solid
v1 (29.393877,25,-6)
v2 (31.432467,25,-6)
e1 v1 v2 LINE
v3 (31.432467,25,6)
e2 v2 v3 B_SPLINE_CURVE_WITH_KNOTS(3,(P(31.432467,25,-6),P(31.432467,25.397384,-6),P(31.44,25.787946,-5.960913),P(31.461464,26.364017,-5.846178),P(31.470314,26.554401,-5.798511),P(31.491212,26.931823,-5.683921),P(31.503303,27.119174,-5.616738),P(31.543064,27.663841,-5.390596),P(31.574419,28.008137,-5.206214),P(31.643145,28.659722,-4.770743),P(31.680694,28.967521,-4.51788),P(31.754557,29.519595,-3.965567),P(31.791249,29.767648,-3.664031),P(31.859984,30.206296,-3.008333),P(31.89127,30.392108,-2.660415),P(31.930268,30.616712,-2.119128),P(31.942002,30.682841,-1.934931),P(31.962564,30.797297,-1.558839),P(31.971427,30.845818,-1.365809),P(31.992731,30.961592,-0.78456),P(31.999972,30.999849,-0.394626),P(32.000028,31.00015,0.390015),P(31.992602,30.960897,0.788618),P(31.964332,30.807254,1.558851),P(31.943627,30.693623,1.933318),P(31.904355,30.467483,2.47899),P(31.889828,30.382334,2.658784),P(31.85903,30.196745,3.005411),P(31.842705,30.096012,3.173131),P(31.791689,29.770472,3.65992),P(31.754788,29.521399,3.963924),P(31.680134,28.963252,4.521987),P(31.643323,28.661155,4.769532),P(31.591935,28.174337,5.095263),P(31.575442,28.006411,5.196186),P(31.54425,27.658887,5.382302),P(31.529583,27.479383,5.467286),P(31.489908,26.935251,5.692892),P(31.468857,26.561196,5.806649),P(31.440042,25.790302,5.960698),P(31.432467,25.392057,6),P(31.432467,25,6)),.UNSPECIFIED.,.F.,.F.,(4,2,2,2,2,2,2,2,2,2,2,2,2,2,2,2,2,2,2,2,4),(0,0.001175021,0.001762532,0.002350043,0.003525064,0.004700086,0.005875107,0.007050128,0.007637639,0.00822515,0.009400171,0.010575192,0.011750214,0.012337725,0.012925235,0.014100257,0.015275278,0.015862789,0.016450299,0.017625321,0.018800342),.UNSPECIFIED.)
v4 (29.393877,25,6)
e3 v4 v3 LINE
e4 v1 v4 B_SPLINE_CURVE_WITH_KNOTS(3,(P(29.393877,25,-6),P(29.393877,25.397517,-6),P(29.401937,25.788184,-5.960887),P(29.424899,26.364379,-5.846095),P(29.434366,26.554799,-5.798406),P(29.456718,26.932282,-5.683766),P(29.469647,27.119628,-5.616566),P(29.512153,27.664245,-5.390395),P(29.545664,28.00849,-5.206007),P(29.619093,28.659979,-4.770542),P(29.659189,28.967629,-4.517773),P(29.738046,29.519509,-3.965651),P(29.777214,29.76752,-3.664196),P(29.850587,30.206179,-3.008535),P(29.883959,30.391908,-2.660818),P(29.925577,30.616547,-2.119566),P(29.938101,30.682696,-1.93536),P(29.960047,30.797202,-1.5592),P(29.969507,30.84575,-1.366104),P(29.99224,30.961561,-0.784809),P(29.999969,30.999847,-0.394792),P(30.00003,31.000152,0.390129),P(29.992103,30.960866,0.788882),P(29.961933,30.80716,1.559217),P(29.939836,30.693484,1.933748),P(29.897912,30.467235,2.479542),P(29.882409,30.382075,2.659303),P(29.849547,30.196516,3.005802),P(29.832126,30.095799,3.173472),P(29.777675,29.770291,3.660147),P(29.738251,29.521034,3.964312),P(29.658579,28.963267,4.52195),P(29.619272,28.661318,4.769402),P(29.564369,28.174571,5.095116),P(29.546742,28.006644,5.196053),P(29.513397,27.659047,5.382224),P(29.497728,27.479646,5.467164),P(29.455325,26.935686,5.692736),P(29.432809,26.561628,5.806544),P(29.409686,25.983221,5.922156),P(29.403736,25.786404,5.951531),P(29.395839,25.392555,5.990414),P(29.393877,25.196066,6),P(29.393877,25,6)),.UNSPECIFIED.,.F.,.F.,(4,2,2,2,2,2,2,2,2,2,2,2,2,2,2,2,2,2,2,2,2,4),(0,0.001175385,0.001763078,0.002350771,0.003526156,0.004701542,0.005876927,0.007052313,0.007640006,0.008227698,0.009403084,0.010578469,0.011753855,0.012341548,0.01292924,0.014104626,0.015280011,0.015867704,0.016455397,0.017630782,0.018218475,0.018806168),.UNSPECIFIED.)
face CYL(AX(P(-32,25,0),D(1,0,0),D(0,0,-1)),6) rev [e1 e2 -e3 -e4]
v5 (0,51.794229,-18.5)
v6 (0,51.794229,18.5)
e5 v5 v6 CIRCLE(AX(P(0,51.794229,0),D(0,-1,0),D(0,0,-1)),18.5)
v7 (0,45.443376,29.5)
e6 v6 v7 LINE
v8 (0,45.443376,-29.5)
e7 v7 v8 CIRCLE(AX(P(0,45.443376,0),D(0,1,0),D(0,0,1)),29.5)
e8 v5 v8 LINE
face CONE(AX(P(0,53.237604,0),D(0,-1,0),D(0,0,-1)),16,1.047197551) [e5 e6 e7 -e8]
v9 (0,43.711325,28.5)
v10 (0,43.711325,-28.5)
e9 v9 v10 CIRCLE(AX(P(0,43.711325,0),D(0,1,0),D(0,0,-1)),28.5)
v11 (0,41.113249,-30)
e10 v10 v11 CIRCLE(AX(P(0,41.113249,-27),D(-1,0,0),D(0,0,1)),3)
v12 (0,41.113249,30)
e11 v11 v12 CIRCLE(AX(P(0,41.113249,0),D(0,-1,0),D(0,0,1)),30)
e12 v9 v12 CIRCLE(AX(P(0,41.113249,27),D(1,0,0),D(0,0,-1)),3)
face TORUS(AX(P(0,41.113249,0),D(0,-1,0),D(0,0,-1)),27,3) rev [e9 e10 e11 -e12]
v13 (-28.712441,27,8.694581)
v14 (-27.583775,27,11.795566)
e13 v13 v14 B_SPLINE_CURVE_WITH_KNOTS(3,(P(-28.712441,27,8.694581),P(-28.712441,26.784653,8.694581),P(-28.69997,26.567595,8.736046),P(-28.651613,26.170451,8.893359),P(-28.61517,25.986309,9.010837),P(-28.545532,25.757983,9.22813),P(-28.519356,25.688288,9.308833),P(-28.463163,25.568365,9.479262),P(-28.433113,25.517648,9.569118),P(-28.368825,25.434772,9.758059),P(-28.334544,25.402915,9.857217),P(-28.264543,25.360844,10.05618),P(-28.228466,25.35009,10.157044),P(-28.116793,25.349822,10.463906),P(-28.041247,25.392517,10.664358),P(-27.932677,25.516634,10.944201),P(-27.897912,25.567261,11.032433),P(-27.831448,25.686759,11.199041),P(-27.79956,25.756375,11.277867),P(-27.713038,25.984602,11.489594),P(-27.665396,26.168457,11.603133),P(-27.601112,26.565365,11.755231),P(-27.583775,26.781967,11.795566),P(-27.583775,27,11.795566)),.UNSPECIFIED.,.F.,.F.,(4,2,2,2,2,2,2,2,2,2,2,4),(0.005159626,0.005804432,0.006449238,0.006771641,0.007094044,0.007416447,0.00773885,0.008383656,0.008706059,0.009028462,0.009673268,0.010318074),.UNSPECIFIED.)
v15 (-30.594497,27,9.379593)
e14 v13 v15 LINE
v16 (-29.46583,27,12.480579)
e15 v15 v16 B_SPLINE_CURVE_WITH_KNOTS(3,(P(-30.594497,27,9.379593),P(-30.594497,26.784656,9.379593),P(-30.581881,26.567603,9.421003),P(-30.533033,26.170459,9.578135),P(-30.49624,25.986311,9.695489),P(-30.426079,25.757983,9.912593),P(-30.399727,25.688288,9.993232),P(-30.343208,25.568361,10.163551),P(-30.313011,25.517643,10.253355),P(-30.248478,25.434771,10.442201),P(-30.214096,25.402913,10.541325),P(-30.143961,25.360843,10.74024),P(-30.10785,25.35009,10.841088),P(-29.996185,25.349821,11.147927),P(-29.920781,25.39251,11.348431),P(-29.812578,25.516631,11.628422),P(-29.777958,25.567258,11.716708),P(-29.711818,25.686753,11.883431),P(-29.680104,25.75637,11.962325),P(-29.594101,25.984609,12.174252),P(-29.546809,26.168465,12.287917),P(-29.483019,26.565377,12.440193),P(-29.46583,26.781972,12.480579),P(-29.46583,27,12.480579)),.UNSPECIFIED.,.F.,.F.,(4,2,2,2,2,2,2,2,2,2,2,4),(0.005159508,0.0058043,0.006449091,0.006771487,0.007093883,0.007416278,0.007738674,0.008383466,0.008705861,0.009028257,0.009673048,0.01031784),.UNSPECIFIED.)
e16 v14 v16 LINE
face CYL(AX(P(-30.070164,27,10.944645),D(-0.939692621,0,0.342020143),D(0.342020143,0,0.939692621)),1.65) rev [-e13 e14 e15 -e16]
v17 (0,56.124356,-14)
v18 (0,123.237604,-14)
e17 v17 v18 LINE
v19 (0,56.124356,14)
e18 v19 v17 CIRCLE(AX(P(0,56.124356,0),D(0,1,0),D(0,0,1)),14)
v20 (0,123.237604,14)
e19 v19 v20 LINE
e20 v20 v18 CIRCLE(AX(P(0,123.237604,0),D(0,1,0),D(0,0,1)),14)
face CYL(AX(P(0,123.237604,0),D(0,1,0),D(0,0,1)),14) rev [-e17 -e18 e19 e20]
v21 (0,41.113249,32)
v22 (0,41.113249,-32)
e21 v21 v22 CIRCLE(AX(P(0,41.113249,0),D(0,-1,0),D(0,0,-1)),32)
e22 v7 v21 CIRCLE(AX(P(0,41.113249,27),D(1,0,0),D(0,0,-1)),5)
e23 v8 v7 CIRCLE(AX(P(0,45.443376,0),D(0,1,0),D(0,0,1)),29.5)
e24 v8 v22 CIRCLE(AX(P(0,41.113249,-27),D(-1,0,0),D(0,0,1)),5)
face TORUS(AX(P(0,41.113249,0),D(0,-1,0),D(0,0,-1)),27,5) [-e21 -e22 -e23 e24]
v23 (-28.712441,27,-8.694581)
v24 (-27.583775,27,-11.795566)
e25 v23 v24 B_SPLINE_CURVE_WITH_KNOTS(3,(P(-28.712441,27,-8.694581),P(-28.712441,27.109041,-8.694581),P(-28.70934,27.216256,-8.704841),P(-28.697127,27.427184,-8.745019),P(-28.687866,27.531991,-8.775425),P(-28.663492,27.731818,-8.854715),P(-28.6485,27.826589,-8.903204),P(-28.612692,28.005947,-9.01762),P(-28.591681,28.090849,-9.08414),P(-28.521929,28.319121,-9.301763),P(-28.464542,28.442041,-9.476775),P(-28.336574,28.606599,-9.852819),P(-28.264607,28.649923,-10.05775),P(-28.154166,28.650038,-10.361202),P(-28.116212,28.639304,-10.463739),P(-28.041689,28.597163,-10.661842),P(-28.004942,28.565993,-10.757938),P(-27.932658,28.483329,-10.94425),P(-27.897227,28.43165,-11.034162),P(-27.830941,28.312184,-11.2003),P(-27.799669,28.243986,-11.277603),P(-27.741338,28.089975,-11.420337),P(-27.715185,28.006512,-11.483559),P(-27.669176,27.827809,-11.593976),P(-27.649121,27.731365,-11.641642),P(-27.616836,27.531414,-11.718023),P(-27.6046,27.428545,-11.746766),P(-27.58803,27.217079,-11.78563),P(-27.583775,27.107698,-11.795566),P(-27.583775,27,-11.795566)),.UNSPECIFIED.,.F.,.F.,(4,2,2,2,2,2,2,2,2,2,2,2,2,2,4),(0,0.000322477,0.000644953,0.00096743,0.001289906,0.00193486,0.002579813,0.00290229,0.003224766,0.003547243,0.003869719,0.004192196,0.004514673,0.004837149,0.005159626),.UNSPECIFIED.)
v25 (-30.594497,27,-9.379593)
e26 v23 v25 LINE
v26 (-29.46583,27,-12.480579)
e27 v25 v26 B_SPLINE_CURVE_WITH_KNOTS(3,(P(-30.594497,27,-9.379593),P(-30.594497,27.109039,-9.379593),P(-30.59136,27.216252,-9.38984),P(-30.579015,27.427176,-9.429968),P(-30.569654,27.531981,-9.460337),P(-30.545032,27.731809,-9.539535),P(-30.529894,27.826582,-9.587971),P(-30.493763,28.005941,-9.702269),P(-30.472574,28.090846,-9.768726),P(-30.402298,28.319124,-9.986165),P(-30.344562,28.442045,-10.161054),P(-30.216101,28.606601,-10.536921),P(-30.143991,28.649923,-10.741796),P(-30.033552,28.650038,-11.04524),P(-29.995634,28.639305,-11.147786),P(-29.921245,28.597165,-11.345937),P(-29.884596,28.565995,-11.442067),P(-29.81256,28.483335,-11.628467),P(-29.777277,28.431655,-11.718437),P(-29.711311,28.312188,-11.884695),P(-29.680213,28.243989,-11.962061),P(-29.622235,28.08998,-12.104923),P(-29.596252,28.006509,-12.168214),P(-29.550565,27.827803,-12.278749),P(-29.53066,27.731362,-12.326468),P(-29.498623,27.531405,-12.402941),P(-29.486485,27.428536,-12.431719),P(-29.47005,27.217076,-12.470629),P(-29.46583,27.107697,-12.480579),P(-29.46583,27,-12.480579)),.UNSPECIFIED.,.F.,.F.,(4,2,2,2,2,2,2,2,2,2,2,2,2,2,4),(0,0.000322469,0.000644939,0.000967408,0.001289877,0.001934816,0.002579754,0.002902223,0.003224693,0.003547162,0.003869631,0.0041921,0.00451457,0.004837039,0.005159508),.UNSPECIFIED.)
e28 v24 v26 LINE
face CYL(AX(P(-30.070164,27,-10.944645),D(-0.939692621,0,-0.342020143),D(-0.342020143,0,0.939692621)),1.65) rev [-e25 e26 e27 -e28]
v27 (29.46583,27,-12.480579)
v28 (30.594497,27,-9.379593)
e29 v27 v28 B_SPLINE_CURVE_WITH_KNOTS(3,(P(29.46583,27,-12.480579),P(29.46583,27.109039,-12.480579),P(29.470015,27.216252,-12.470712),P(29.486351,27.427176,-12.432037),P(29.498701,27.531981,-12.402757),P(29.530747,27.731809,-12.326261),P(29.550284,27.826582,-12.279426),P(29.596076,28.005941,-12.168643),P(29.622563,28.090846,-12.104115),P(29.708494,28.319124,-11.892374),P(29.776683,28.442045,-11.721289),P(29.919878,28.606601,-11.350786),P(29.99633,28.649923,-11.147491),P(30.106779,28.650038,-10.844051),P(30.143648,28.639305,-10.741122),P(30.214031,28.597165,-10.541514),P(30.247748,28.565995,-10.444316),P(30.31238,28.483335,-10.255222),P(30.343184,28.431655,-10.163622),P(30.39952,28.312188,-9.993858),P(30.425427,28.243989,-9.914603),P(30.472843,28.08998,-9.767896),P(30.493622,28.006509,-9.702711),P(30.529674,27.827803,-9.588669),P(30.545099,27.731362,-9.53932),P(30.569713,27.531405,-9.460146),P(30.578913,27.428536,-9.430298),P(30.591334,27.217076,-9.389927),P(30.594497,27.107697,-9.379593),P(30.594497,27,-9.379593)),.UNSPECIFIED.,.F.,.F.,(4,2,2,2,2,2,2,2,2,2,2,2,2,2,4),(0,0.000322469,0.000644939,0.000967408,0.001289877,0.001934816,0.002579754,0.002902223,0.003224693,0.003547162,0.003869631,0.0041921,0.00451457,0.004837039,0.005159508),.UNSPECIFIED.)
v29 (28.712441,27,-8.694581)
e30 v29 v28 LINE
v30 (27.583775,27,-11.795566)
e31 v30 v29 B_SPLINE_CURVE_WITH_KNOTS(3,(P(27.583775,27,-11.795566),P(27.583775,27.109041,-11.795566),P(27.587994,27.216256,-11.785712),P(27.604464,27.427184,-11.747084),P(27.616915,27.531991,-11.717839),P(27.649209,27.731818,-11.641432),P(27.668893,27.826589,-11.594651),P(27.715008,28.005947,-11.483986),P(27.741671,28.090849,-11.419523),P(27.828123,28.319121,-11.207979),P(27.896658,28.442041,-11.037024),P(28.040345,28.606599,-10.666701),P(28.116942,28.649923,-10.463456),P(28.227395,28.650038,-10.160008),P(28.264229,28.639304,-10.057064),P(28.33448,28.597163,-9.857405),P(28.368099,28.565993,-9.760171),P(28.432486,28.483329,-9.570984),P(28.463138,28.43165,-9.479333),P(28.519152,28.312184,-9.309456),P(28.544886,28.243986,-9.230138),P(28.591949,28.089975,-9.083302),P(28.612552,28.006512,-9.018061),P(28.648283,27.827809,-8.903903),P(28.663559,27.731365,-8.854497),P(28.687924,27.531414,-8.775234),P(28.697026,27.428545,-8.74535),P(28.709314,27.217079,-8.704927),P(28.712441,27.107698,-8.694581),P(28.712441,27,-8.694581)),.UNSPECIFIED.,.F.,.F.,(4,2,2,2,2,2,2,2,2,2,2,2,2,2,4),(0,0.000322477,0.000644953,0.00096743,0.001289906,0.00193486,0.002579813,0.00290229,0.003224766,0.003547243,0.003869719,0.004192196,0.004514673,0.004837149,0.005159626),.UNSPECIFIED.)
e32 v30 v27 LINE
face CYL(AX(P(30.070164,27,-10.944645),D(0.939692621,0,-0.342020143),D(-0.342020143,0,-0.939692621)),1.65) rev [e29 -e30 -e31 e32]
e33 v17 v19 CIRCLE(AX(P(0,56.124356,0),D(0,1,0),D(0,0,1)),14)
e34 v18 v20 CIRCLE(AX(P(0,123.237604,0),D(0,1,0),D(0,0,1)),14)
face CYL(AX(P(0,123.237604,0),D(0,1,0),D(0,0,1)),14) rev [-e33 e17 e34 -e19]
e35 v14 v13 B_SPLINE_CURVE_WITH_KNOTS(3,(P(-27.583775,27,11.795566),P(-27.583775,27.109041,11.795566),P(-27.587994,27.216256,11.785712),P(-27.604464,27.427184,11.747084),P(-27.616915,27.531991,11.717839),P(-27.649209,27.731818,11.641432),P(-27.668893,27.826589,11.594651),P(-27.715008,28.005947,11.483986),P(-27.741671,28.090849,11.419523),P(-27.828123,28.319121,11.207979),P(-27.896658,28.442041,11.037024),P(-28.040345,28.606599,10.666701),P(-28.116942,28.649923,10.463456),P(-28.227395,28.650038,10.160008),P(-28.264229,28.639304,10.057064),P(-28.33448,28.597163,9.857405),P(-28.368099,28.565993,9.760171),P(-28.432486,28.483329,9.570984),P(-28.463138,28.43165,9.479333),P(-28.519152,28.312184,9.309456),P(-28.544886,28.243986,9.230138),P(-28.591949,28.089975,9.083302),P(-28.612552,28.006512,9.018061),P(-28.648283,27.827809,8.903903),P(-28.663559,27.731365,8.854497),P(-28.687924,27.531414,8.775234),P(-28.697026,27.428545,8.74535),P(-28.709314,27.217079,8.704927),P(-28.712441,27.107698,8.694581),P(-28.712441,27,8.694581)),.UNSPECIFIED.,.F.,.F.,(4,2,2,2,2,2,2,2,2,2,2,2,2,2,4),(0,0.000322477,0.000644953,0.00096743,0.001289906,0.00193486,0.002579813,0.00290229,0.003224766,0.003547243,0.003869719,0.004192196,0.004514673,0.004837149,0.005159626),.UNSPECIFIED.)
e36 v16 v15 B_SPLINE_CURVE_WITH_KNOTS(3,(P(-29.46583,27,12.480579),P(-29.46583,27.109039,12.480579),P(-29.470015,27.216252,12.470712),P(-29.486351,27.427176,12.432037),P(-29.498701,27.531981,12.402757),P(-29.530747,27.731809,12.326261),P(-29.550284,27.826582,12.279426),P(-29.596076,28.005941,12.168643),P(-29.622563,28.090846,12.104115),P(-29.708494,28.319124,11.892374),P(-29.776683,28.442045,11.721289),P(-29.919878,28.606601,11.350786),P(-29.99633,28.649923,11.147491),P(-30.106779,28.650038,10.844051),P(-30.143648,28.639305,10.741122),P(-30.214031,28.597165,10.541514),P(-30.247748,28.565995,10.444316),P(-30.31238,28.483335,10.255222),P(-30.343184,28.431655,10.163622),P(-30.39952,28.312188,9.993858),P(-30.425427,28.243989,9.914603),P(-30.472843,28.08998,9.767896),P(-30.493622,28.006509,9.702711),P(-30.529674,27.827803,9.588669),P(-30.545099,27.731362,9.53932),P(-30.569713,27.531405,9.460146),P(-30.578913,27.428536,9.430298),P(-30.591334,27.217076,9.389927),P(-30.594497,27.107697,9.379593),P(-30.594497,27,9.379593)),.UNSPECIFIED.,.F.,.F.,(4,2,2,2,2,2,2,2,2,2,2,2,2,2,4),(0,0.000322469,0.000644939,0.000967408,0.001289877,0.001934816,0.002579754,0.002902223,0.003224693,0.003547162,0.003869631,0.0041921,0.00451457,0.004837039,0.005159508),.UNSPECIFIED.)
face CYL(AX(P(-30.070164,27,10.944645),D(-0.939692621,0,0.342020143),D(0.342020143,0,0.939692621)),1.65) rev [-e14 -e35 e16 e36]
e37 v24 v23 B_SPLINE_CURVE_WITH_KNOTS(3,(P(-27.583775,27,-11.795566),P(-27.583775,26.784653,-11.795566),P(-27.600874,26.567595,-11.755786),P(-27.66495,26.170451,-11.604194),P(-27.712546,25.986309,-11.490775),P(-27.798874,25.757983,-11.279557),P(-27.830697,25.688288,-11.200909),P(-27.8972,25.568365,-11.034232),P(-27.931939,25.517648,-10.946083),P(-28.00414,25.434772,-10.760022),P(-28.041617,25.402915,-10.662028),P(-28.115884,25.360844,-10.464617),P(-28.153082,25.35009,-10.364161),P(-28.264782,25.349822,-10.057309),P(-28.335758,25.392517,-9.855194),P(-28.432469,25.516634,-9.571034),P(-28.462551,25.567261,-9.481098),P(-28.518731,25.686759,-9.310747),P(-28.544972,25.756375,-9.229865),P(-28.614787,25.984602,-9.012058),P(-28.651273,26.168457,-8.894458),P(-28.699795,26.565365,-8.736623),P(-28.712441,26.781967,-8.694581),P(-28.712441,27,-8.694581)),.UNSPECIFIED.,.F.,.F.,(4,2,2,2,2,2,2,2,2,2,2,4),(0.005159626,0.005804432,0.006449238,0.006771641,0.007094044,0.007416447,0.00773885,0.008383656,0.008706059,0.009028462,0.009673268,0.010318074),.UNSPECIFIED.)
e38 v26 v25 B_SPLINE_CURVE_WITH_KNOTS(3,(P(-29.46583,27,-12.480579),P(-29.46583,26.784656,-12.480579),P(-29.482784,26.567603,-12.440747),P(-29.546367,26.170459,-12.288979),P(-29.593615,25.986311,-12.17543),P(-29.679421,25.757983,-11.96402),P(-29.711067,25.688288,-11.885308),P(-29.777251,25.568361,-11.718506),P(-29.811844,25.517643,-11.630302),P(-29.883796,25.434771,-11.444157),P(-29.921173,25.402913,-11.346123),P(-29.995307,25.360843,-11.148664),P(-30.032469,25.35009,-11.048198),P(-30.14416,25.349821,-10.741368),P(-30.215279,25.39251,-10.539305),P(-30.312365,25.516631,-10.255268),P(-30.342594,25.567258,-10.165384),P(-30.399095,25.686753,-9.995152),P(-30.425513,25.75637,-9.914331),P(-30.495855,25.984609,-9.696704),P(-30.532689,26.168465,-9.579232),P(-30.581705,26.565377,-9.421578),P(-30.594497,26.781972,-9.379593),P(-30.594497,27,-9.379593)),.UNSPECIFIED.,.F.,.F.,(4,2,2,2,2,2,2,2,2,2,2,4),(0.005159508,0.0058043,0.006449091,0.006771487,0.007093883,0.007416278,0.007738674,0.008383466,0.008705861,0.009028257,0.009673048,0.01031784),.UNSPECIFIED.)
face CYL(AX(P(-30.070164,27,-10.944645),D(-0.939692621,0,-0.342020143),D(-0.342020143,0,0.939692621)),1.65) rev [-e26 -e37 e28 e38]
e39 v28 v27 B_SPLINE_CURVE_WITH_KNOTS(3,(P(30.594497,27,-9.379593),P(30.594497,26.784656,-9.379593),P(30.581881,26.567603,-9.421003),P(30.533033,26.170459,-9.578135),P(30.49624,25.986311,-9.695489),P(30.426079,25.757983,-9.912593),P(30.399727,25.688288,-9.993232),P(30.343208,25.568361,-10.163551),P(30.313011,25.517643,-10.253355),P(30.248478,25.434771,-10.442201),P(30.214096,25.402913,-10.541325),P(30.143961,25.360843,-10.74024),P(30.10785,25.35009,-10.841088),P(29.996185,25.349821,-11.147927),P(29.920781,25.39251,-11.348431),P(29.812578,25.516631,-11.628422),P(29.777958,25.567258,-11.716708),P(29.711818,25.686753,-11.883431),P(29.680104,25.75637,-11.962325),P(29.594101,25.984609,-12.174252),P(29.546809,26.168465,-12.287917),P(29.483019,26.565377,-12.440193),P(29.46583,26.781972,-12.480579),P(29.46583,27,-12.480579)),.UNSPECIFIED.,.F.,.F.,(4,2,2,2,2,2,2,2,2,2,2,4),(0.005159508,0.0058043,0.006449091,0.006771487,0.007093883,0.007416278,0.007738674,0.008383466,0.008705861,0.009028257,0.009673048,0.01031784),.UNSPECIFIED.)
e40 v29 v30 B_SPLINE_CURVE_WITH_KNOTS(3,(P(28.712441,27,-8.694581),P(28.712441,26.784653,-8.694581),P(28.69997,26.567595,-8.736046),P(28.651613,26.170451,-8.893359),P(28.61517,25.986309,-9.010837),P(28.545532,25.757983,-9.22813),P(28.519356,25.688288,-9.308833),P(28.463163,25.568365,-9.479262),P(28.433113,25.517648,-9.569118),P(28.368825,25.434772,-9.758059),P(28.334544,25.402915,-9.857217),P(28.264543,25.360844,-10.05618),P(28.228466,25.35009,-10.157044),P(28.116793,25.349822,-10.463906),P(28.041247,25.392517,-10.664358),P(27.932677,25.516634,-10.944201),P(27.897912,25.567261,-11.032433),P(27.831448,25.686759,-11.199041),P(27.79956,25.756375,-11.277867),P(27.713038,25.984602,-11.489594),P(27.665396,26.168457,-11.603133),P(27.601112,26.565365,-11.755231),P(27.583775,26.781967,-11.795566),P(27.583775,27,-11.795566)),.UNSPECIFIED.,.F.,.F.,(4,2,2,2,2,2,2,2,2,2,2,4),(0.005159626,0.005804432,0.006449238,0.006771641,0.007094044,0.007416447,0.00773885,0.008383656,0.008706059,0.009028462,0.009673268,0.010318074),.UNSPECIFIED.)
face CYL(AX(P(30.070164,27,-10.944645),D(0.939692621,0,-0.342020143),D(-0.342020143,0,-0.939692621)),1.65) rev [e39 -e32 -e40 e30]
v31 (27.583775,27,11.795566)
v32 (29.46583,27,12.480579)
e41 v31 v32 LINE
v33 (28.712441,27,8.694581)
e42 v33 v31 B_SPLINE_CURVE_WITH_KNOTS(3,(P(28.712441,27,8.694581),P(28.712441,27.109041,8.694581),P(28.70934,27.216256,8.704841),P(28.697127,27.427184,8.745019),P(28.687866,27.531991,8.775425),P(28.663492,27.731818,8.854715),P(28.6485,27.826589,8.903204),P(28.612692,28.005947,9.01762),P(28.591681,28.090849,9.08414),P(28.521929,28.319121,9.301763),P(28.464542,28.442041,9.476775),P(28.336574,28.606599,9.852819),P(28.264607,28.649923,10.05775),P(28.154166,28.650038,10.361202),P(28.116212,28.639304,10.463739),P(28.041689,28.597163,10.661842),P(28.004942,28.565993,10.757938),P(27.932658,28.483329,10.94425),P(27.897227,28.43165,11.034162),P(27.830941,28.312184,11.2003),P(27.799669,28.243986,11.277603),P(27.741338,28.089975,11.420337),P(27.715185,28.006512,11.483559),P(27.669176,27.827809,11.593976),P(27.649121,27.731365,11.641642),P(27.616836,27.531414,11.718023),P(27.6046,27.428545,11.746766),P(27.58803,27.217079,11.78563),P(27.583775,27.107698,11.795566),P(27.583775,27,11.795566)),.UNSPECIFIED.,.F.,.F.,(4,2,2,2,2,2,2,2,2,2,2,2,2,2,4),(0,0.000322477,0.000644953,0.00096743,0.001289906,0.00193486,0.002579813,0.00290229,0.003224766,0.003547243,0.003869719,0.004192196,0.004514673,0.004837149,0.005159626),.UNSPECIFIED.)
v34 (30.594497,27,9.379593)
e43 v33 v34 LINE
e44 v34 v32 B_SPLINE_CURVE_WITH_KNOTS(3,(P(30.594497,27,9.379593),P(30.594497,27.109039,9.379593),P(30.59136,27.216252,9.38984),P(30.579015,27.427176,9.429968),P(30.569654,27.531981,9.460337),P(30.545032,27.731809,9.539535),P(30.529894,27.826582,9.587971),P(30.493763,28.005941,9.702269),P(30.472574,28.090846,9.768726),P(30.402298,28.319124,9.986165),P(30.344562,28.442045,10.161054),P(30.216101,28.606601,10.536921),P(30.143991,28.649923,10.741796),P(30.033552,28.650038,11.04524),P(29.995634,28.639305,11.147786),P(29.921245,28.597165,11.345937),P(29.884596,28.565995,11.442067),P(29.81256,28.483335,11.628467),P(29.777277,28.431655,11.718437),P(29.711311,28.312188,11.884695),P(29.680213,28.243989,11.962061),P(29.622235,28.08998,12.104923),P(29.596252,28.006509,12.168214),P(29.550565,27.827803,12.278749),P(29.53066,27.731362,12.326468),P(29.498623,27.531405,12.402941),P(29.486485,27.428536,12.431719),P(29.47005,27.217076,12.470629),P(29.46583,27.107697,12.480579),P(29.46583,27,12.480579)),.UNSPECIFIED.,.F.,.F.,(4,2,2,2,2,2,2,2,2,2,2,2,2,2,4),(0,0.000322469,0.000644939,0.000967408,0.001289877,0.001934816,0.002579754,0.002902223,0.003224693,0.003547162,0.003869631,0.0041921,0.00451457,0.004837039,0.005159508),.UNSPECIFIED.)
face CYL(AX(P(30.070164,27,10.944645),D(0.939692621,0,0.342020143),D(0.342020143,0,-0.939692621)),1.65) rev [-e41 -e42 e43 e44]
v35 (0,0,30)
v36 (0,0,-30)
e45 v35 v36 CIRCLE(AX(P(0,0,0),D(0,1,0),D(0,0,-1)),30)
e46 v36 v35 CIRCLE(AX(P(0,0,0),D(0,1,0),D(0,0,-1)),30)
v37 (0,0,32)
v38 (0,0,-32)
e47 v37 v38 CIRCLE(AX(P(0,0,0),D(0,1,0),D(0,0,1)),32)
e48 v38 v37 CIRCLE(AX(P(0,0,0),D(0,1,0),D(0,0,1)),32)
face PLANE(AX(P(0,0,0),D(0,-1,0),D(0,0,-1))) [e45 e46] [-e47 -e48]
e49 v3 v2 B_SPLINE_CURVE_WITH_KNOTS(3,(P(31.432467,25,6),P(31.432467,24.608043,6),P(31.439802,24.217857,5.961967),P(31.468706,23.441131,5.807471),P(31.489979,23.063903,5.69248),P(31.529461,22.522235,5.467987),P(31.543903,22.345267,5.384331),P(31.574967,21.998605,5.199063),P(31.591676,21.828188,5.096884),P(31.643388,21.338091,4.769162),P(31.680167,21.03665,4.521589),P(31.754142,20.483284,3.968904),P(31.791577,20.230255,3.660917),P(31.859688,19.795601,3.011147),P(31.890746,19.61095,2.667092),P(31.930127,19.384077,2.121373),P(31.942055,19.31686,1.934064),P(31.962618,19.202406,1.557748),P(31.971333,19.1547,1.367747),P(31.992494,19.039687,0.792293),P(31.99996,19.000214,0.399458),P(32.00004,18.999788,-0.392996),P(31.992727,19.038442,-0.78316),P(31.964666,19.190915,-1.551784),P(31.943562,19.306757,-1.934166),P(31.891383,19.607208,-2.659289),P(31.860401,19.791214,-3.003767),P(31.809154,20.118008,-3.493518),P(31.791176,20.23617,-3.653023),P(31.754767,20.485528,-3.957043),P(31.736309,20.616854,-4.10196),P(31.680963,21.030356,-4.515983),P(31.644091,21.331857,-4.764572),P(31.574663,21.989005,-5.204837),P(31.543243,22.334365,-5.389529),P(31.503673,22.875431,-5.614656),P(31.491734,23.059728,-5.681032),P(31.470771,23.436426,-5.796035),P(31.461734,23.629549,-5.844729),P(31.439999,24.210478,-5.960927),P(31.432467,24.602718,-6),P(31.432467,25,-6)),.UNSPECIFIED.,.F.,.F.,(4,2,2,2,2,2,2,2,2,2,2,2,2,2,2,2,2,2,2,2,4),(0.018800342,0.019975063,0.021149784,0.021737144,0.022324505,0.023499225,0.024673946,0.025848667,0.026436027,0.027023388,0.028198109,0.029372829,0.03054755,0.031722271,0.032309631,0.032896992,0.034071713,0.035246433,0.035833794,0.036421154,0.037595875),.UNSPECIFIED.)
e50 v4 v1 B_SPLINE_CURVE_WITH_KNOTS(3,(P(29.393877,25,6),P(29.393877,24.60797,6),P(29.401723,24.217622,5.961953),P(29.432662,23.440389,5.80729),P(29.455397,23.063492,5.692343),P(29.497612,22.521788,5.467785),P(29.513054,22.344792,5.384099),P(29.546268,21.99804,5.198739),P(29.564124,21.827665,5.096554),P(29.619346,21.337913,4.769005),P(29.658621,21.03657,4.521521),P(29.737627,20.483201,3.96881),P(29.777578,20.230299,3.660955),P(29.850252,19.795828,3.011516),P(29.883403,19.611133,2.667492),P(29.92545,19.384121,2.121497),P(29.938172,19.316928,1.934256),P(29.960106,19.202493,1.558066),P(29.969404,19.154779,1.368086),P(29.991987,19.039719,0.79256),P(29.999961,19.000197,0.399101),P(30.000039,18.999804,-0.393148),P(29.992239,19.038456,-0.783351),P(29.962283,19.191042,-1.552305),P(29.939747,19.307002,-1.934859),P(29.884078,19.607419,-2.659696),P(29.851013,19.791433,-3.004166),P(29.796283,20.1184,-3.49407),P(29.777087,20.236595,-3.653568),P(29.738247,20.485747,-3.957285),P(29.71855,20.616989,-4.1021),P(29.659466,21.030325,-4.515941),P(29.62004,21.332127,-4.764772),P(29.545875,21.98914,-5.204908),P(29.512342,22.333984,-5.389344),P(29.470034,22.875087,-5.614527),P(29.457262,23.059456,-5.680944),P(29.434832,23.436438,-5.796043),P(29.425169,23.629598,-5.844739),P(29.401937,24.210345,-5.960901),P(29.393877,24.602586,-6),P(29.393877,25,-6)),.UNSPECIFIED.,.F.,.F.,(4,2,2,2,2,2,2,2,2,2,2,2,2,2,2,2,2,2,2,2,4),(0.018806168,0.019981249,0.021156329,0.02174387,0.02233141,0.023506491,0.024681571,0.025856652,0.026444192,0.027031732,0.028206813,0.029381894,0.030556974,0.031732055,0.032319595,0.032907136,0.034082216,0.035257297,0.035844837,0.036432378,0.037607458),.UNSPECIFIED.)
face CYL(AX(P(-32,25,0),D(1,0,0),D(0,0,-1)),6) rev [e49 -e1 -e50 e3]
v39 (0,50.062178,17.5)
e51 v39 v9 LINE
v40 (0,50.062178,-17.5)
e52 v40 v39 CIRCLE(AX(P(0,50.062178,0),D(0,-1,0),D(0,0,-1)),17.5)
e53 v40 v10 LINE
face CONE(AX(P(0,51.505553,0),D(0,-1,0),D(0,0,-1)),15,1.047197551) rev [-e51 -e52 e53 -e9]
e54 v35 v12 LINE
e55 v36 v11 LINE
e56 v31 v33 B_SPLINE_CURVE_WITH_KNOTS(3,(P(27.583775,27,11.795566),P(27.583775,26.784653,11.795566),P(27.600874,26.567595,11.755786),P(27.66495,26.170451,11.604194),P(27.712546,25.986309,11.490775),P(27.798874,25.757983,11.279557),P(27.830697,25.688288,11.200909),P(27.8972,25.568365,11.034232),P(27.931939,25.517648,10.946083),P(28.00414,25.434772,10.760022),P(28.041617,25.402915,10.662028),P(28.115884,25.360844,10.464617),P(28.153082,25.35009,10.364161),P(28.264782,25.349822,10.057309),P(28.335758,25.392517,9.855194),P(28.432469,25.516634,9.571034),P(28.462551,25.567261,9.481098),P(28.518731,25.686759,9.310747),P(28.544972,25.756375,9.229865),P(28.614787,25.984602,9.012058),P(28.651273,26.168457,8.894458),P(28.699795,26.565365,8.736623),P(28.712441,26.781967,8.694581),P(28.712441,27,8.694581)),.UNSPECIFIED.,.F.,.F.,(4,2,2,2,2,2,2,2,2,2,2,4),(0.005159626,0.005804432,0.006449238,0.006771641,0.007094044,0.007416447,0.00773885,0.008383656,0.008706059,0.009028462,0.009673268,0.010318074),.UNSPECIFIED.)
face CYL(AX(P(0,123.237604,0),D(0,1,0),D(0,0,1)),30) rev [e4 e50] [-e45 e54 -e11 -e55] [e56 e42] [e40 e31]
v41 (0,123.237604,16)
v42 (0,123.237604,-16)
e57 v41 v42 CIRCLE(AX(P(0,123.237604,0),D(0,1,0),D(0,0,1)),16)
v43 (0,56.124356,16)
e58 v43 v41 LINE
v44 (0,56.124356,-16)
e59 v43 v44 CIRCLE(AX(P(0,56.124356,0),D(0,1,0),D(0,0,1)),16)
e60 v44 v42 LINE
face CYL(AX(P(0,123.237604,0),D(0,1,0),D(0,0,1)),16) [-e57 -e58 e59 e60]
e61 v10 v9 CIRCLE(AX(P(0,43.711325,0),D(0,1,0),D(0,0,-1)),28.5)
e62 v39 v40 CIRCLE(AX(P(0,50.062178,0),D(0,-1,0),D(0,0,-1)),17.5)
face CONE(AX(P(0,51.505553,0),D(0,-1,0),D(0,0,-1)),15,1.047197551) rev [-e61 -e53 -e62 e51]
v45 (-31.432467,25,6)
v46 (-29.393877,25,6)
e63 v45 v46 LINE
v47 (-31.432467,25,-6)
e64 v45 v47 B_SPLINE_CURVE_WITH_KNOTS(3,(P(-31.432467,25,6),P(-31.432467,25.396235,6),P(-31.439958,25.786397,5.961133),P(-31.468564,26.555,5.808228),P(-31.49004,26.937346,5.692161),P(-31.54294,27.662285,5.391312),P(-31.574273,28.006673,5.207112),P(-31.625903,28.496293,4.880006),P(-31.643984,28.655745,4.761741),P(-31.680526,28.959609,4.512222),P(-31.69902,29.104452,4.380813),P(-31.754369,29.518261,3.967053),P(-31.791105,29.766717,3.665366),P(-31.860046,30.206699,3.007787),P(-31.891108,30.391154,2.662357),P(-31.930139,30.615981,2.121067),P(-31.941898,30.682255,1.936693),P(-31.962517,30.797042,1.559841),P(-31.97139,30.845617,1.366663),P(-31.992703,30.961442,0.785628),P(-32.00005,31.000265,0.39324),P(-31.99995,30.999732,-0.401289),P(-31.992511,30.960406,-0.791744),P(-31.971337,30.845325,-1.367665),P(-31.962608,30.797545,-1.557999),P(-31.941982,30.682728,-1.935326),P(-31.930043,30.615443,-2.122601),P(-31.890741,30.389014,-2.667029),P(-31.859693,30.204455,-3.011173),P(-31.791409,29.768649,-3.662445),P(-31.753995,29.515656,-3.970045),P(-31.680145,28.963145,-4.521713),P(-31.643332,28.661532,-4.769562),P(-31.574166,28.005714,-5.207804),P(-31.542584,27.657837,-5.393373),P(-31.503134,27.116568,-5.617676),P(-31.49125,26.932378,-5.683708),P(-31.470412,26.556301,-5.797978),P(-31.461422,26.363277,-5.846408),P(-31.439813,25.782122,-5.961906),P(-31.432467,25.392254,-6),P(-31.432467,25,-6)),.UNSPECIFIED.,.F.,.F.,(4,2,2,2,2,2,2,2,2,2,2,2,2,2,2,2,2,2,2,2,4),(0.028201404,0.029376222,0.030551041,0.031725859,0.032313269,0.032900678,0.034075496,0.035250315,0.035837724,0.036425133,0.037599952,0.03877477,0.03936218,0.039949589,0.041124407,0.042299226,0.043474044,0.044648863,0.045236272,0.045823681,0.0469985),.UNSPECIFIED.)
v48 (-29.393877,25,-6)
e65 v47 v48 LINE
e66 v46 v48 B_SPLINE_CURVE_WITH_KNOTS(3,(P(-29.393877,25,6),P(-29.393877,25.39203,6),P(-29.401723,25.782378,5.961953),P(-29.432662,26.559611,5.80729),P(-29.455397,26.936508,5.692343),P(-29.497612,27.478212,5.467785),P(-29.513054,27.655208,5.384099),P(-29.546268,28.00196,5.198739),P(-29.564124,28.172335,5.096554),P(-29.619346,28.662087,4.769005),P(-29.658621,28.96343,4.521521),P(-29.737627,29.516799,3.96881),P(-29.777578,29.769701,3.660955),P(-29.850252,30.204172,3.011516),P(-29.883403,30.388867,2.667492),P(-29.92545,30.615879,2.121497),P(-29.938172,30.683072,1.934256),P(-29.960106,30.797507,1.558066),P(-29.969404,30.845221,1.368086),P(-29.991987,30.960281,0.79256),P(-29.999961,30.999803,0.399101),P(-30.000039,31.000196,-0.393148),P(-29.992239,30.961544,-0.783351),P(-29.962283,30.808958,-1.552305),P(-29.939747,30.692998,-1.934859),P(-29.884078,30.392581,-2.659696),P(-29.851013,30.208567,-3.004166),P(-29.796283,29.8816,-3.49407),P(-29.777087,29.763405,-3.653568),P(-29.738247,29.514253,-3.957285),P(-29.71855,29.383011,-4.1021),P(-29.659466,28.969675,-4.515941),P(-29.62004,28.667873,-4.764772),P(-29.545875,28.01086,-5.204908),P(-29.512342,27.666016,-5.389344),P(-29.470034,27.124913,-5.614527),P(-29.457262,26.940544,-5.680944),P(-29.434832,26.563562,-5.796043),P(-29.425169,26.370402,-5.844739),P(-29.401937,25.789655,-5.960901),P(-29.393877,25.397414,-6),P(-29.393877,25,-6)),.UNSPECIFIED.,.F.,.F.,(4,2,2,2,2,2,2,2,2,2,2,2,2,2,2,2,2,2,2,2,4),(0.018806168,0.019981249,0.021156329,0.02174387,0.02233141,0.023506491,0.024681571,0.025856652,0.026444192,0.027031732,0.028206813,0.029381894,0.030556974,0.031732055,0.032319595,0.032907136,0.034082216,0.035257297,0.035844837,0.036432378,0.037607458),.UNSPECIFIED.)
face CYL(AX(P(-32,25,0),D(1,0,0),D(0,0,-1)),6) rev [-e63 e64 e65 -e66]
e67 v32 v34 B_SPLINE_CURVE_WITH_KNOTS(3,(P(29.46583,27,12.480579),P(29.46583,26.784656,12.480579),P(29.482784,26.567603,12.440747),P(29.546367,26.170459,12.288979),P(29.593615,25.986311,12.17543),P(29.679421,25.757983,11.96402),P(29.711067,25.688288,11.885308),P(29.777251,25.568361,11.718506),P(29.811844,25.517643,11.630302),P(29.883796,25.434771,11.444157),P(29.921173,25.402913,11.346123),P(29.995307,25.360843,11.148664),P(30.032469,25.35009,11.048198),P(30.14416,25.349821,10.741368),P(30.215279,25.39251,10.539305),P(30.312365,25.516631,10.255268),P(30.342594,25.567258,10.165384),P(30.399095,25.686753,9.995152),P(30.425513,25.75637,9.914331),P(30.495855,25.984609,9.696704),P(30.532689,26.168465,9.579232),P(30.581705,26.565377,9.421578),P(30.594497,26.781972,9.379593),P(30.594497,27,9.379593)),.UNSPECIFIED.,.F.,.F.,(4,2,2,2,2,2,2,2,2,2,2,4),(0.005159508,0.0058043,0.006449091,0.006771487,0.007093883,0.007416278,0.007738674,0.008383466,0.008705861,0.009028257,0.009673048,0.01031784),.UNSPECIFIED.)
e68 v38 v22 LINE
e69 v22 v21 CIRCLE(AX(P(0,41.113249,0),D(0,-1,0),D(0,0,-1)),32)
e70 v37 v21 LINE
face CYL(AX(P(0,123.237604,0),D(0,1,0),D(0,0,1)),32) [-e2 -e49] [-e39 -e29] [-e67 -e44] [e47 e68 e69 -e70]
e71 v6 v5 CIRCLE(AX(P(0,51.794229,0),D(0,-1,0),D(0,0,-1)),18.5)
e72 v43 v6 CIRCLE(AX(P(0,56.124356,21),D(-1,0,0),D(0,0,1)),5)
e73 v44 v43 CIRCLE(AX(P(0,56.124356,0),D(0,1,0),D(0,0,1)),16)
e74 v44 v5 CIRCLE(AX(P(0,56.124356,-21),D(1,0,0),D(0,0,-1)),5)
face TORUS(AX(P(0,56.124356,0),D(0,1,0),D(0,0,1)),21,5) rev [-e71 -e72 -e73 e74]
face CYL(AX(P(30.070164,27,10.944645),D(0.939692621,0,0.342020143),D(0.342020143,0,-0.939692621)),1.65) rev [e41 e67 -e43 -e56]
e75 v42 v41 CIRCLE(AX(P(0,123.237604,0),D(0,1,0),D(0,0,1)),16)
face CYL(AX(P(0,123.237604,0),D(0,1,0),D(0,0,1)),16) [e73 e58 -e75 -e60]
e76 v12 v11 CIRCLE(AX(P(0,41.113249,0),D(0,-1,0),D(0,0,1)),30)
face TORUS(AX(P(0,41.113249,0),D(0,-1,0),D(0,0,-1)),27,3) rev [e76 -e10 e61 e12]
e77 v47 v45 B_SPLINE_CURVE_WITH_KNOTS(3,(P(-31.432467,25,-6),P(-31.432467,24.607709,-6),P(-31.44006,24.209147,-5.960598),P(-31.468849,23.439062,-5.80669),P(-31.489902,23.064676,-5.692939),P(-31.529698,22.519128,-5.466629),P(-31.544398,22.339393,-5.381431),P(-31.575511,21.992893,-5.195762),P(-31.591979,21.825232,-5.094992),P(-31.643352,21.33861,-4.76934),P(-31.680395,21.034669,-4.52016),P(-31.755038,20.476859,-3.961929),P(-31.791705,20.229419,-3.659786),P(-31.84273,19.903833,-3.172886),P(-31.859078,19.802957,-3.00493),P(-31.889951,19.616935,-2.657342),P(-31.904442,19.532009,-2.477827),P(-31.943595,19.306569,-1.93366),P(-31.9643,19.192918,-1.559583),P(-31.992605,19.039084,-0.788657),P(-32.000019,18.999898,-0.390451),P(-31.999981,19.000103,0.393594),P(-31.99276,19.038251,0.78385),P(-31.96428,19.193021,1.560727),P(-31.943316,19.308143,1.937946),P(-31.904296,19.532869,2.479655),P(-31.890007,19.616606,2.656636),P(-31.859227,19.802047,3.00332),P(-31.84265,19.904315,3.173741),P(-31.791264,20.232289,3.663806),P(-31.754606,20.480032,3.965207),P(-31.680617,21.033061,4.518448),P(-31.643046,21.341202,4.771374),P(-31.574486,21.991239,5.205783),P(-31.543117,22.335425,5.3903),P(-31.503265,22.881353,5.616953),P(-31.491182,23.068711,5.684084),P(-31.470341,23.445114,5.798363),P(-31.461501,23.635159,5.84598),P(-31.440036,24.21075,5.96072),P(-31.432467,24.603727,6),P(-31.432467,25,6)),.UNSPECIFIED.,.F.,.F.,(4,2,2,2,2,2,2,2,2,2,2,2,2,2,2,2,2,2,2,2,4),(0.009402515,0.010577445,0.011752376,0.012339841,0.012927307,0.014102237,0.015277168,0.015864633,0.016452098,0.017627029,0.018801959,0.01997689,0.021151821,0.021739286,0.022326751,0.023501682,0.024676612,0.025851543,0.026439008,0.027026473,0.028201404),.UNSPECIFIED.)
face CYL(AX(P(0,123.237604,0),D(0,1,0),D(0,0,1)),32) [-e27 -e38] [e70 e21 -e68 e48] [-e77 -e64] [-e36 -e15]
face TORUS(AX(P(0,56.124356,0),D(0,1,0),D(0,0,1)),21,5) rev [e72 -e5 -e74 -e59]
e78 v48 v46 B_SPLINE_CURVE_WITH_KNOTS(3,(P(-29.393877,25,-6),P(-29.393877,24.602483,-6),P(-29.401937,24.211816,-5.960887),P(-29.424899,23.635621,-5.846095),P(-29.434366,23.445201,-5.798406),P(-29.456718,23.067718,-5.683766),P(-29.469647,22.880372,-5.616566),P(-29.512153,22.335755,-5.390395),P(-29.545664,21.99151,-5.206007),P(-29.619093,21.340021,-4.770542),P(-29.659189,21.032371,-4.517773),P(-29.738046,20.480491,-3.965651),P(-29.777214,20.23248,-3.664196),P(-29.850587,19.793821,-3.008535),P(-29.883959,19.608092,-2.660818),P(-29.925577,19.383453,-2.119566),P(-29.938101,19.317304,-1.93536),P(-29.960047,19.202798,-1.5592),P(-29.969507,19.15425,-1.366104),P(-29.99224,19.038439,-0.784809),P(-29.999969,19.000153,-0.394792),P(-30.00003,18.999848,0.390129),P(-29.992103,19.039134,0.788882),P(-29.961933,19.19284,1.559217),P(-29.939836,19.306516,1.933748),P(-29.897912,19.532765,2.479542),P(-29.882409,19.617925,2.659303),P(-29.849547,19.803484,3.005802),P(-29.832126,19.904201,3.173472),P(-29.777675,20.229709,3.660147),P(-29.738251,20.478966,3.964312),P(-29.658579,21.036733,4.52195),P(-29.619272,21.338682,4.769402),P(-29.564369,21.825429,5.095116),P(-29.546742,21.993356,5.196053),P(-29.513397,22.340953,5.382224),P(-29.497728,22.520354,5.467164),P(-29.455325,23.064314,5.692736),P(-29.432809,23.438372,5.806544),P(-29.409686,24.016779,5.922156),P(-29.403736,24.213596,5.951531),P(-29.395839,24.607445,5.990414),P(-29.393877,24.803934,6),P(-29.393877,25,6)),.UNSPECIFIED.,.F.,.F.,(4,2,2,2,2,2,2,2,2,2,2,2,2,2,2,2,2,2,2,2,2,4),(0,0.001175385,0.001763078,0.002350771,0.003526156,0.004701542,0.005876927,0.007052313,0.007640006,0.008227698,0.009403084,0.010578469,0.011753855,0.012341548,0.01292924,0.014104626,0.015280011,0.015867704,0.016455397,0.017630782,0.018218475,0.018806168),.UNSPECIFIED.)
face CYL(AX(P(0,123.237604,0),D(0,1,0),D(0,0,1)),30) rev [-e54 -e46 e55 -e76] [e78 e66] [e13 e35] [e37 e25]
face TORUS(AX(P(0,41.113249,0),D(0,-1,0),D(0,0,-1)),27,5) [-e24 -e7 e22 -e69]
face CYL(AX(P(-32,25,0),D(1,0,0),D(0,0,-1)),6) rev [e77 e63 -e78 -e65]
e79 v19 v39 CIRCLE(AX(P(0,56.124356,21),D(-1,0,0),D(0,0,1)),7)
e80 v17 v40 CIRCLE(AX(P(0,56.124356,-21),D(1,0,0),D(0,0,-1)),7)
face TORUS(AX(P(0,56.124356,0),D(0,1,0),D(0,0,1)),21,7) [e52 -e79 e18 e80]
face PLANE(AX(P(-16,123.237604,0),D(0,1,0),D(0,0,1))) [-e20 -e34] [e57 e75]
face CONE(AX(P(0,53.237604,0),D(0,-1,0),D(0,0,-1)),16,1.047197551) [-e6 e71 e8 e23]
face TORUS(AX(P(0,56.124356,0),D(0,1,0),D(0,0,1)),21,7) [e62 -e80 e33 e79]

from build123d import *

# Parameters (mm, degrees)
FILLET1_R                       = 5
SHELL1_T                        = -2
CUT_EXTRUDE1_DEPTH              = 132.284070659
CUT_EXTRUDE1_DEPTH_BACK         = 132.284070659
SKETCH6_R                       = 6
M4_TAPPED_HOLE1_D               = 3.3
M4_TAPPED_HOLE1_DEPTH           = 10.1
M4_TAPPED_HOLE1_TIP             = 0.991420021
M4_TAPPED_HOLE1_ON_FACE_2_D     = 3.3
M4_TAPPED_HOLE1_ON_FACE_2_DEPTH = 10.1
M4_TAPPED_HOLE1_ON_FACE_2_TIP   = 0.991420021
M4_TAPPED_HOLE1_ON_FACE_3_D     = 3.3
M4_TAPPED_HOLE1_ON_FACE_3_DEPTH = 10.1
M4_TAPPED_HOLE1_ON_FACE_3_TIP   = 0.991420021
M4_TAPPED_HOLE1_ON_FACE_4_D     = 3.3
M4_TAPPED_HOLE1_ON_FACE_4_DEPTH = 10.1
M4_TAPPED_HOLE1_ON_FACE_4_TIP   = 0.991420021


with BuildPart() as part:
    # Sketch1 → Revolve1 (revolve)
    with BuildSketch(Plane.XY, mode=Mode.PRIVATE) as revolve1_sk:
        Polygon((0, 0), (-32, 0), (-32, 44), (-16, 53.237604307), (-16, 123.237604307), (0, 123.237604307), align=None)
    revolve(revolve1_sk.sketch.rotate(Axis((0, 123.237604307, 0), (0, -1, 0)), 270), axis=Axis((0, 123.237604307, 0), (0, -1, 0)))

    # Fillet1
    fillet1_edges = [part.edges().sort_by_distance(p)[0] for p in [
        (0, 53.237604307, -16),
        (0, 44, -32),
    ]]
    fillet(fillet1_edges, radius=FILLET1_R)

    # Shell1
    shell1_openings = [part.faces().sort_by_distance(p)[0] for p in [
        (0, 123.237604307, 0),
        (0, 0, 0),
    ]]
    offset(amount=SHELL1_T, openings=shell1_openings, kind=Kind.INTERSECTION)

    # Sketch6 → Cut-Extrude1 (cut, two sides: drawn at the far end of the back side and taken through both)
    with BuildSketch(Plane(origin=(0, 0, 0), x_dir=(0, 0, -1), z_dir=(1, 0, 0)).offset(-CUT_EXTRUDE1_DEPTH_BACK)):
        with Locations((0, 25)):
            Circle(SKETCH6_R)
    extrude(amount=CUT_EXTRUDE1_DEPTH + CUT_EXTRUDE1_DEPTH_BACK, mode=Mode.SUBTRACT)

    # M4 Tapped Hole1
    with Locations(Plane(origin=(-30.070163865, 27, -10.944644586), x_dir=(0.342020143326, 0, -0.939692620786), z_dir=(-0.939692620786, 0, -0.342020143326))):
        with Locations((0, 0)):
            Hole(M4_TAPPED_HOLE1_D / 2, depth=M4_TAPPED_HOLE1_DEPTH)
            with Locations((0, 0, -(M4_TAPPED_HOLE1_DEPTH + M4_TAPPED_HOLE1_TIP / 2))):  # 118° drill point
                Cone(0, M4_TAPPED_HOLE1_D / 2, M4_TAPPED_HOLE1_TIP, mode=Mode.SUBTRACT)

    # M4 Tapped Hole1 on face 2
    with Locations(Plane(origin=(-30.070163865, 27, 10.944644586), x_dir=(-0.342019894889, 0, -0.939692711209), z_dir=(-0.939692711209, 0, 0.342019894889))):
        with Locations((0, 0)):
            Hole(M4_TAPPED_HOLE1_ON_FACE_2_D / 2, depth=M4_TAPPED_HOLE1_ON_FACE_2_DEPTH)
            with Locations((0, 0, -(M4_TAPPED_HOLE1_ON_FACE_2_DEPTH + M4_TAPPED_HOLE1_ON_FACE_2_TIP / 2))):  # 118° drill point
                Cone(0, M4_TAPPED_HOLE1_ON_FACE_2_D / 2, M4_TAPPED_HOLE1_ON_FACE_2_TIP, mode=Mode.SUBTRACT)

    # M4 Tapped Hole1 on face 3
    with Locations(Plane(origin=(30.070163865, 27, -10.944644586), x_dir=(0.342019894889, 0, 0.939692711209), z_dir=(0.939692711209, 0, -0.342019894889))):
        with Locations((0, 0)):
            Hole(M4_TAPPED_HOLE1_ON_FACE_3_D / 2, depth=M4_TAPPED_HOLE1_ON_FACE_3_DEPTH)
            with Locations((0, 0, -(M4_TAPPED_HOLE1_ON_FACE_3_DEPTH + M4_TAPPED_HOLE1_ON_FACE_3_TIP / 2))):  # 118° drill point
                Cone(0, M4_TAPPED_HOLE1_ON_FACE_3_D / 2, M4_TAPPED_HOLE1_ON_FACE_3_TIP, mode=Mode.SUBTRACT)

    # M4 Tapped Hole1 on face 4
    with Locations(Plane(origin=(30.070163865, 27, 10.944644586), x_dir=(-0.342019894889, 0, 0.939692711209), z_dir=(0.939692711209, 0, 0.342019894889))):
        with Locations((0, 0)):
            Hole(M4_TAPPED_HOLE1_ON_FACE_4_D / 2, depth=M4_TAPPED_HOLE1_ON_FACE_4_DEPTH)
            with Locations((0, 0, -(M4_TAPPED_HOLE1_ON_FACE_4_DEPTH + M4_TAPPED_HOLE1_ON_FACE_4_TIP / 2))):  # 118° drill point
                Cone(0, M4_TAPPED_HOLE1_ON_FACE_4_D / 2, M4_TAPPED_HOLE1_ON_FACE_4_TIP, mode=Mode.SUBTRACT)


solid = part.part
